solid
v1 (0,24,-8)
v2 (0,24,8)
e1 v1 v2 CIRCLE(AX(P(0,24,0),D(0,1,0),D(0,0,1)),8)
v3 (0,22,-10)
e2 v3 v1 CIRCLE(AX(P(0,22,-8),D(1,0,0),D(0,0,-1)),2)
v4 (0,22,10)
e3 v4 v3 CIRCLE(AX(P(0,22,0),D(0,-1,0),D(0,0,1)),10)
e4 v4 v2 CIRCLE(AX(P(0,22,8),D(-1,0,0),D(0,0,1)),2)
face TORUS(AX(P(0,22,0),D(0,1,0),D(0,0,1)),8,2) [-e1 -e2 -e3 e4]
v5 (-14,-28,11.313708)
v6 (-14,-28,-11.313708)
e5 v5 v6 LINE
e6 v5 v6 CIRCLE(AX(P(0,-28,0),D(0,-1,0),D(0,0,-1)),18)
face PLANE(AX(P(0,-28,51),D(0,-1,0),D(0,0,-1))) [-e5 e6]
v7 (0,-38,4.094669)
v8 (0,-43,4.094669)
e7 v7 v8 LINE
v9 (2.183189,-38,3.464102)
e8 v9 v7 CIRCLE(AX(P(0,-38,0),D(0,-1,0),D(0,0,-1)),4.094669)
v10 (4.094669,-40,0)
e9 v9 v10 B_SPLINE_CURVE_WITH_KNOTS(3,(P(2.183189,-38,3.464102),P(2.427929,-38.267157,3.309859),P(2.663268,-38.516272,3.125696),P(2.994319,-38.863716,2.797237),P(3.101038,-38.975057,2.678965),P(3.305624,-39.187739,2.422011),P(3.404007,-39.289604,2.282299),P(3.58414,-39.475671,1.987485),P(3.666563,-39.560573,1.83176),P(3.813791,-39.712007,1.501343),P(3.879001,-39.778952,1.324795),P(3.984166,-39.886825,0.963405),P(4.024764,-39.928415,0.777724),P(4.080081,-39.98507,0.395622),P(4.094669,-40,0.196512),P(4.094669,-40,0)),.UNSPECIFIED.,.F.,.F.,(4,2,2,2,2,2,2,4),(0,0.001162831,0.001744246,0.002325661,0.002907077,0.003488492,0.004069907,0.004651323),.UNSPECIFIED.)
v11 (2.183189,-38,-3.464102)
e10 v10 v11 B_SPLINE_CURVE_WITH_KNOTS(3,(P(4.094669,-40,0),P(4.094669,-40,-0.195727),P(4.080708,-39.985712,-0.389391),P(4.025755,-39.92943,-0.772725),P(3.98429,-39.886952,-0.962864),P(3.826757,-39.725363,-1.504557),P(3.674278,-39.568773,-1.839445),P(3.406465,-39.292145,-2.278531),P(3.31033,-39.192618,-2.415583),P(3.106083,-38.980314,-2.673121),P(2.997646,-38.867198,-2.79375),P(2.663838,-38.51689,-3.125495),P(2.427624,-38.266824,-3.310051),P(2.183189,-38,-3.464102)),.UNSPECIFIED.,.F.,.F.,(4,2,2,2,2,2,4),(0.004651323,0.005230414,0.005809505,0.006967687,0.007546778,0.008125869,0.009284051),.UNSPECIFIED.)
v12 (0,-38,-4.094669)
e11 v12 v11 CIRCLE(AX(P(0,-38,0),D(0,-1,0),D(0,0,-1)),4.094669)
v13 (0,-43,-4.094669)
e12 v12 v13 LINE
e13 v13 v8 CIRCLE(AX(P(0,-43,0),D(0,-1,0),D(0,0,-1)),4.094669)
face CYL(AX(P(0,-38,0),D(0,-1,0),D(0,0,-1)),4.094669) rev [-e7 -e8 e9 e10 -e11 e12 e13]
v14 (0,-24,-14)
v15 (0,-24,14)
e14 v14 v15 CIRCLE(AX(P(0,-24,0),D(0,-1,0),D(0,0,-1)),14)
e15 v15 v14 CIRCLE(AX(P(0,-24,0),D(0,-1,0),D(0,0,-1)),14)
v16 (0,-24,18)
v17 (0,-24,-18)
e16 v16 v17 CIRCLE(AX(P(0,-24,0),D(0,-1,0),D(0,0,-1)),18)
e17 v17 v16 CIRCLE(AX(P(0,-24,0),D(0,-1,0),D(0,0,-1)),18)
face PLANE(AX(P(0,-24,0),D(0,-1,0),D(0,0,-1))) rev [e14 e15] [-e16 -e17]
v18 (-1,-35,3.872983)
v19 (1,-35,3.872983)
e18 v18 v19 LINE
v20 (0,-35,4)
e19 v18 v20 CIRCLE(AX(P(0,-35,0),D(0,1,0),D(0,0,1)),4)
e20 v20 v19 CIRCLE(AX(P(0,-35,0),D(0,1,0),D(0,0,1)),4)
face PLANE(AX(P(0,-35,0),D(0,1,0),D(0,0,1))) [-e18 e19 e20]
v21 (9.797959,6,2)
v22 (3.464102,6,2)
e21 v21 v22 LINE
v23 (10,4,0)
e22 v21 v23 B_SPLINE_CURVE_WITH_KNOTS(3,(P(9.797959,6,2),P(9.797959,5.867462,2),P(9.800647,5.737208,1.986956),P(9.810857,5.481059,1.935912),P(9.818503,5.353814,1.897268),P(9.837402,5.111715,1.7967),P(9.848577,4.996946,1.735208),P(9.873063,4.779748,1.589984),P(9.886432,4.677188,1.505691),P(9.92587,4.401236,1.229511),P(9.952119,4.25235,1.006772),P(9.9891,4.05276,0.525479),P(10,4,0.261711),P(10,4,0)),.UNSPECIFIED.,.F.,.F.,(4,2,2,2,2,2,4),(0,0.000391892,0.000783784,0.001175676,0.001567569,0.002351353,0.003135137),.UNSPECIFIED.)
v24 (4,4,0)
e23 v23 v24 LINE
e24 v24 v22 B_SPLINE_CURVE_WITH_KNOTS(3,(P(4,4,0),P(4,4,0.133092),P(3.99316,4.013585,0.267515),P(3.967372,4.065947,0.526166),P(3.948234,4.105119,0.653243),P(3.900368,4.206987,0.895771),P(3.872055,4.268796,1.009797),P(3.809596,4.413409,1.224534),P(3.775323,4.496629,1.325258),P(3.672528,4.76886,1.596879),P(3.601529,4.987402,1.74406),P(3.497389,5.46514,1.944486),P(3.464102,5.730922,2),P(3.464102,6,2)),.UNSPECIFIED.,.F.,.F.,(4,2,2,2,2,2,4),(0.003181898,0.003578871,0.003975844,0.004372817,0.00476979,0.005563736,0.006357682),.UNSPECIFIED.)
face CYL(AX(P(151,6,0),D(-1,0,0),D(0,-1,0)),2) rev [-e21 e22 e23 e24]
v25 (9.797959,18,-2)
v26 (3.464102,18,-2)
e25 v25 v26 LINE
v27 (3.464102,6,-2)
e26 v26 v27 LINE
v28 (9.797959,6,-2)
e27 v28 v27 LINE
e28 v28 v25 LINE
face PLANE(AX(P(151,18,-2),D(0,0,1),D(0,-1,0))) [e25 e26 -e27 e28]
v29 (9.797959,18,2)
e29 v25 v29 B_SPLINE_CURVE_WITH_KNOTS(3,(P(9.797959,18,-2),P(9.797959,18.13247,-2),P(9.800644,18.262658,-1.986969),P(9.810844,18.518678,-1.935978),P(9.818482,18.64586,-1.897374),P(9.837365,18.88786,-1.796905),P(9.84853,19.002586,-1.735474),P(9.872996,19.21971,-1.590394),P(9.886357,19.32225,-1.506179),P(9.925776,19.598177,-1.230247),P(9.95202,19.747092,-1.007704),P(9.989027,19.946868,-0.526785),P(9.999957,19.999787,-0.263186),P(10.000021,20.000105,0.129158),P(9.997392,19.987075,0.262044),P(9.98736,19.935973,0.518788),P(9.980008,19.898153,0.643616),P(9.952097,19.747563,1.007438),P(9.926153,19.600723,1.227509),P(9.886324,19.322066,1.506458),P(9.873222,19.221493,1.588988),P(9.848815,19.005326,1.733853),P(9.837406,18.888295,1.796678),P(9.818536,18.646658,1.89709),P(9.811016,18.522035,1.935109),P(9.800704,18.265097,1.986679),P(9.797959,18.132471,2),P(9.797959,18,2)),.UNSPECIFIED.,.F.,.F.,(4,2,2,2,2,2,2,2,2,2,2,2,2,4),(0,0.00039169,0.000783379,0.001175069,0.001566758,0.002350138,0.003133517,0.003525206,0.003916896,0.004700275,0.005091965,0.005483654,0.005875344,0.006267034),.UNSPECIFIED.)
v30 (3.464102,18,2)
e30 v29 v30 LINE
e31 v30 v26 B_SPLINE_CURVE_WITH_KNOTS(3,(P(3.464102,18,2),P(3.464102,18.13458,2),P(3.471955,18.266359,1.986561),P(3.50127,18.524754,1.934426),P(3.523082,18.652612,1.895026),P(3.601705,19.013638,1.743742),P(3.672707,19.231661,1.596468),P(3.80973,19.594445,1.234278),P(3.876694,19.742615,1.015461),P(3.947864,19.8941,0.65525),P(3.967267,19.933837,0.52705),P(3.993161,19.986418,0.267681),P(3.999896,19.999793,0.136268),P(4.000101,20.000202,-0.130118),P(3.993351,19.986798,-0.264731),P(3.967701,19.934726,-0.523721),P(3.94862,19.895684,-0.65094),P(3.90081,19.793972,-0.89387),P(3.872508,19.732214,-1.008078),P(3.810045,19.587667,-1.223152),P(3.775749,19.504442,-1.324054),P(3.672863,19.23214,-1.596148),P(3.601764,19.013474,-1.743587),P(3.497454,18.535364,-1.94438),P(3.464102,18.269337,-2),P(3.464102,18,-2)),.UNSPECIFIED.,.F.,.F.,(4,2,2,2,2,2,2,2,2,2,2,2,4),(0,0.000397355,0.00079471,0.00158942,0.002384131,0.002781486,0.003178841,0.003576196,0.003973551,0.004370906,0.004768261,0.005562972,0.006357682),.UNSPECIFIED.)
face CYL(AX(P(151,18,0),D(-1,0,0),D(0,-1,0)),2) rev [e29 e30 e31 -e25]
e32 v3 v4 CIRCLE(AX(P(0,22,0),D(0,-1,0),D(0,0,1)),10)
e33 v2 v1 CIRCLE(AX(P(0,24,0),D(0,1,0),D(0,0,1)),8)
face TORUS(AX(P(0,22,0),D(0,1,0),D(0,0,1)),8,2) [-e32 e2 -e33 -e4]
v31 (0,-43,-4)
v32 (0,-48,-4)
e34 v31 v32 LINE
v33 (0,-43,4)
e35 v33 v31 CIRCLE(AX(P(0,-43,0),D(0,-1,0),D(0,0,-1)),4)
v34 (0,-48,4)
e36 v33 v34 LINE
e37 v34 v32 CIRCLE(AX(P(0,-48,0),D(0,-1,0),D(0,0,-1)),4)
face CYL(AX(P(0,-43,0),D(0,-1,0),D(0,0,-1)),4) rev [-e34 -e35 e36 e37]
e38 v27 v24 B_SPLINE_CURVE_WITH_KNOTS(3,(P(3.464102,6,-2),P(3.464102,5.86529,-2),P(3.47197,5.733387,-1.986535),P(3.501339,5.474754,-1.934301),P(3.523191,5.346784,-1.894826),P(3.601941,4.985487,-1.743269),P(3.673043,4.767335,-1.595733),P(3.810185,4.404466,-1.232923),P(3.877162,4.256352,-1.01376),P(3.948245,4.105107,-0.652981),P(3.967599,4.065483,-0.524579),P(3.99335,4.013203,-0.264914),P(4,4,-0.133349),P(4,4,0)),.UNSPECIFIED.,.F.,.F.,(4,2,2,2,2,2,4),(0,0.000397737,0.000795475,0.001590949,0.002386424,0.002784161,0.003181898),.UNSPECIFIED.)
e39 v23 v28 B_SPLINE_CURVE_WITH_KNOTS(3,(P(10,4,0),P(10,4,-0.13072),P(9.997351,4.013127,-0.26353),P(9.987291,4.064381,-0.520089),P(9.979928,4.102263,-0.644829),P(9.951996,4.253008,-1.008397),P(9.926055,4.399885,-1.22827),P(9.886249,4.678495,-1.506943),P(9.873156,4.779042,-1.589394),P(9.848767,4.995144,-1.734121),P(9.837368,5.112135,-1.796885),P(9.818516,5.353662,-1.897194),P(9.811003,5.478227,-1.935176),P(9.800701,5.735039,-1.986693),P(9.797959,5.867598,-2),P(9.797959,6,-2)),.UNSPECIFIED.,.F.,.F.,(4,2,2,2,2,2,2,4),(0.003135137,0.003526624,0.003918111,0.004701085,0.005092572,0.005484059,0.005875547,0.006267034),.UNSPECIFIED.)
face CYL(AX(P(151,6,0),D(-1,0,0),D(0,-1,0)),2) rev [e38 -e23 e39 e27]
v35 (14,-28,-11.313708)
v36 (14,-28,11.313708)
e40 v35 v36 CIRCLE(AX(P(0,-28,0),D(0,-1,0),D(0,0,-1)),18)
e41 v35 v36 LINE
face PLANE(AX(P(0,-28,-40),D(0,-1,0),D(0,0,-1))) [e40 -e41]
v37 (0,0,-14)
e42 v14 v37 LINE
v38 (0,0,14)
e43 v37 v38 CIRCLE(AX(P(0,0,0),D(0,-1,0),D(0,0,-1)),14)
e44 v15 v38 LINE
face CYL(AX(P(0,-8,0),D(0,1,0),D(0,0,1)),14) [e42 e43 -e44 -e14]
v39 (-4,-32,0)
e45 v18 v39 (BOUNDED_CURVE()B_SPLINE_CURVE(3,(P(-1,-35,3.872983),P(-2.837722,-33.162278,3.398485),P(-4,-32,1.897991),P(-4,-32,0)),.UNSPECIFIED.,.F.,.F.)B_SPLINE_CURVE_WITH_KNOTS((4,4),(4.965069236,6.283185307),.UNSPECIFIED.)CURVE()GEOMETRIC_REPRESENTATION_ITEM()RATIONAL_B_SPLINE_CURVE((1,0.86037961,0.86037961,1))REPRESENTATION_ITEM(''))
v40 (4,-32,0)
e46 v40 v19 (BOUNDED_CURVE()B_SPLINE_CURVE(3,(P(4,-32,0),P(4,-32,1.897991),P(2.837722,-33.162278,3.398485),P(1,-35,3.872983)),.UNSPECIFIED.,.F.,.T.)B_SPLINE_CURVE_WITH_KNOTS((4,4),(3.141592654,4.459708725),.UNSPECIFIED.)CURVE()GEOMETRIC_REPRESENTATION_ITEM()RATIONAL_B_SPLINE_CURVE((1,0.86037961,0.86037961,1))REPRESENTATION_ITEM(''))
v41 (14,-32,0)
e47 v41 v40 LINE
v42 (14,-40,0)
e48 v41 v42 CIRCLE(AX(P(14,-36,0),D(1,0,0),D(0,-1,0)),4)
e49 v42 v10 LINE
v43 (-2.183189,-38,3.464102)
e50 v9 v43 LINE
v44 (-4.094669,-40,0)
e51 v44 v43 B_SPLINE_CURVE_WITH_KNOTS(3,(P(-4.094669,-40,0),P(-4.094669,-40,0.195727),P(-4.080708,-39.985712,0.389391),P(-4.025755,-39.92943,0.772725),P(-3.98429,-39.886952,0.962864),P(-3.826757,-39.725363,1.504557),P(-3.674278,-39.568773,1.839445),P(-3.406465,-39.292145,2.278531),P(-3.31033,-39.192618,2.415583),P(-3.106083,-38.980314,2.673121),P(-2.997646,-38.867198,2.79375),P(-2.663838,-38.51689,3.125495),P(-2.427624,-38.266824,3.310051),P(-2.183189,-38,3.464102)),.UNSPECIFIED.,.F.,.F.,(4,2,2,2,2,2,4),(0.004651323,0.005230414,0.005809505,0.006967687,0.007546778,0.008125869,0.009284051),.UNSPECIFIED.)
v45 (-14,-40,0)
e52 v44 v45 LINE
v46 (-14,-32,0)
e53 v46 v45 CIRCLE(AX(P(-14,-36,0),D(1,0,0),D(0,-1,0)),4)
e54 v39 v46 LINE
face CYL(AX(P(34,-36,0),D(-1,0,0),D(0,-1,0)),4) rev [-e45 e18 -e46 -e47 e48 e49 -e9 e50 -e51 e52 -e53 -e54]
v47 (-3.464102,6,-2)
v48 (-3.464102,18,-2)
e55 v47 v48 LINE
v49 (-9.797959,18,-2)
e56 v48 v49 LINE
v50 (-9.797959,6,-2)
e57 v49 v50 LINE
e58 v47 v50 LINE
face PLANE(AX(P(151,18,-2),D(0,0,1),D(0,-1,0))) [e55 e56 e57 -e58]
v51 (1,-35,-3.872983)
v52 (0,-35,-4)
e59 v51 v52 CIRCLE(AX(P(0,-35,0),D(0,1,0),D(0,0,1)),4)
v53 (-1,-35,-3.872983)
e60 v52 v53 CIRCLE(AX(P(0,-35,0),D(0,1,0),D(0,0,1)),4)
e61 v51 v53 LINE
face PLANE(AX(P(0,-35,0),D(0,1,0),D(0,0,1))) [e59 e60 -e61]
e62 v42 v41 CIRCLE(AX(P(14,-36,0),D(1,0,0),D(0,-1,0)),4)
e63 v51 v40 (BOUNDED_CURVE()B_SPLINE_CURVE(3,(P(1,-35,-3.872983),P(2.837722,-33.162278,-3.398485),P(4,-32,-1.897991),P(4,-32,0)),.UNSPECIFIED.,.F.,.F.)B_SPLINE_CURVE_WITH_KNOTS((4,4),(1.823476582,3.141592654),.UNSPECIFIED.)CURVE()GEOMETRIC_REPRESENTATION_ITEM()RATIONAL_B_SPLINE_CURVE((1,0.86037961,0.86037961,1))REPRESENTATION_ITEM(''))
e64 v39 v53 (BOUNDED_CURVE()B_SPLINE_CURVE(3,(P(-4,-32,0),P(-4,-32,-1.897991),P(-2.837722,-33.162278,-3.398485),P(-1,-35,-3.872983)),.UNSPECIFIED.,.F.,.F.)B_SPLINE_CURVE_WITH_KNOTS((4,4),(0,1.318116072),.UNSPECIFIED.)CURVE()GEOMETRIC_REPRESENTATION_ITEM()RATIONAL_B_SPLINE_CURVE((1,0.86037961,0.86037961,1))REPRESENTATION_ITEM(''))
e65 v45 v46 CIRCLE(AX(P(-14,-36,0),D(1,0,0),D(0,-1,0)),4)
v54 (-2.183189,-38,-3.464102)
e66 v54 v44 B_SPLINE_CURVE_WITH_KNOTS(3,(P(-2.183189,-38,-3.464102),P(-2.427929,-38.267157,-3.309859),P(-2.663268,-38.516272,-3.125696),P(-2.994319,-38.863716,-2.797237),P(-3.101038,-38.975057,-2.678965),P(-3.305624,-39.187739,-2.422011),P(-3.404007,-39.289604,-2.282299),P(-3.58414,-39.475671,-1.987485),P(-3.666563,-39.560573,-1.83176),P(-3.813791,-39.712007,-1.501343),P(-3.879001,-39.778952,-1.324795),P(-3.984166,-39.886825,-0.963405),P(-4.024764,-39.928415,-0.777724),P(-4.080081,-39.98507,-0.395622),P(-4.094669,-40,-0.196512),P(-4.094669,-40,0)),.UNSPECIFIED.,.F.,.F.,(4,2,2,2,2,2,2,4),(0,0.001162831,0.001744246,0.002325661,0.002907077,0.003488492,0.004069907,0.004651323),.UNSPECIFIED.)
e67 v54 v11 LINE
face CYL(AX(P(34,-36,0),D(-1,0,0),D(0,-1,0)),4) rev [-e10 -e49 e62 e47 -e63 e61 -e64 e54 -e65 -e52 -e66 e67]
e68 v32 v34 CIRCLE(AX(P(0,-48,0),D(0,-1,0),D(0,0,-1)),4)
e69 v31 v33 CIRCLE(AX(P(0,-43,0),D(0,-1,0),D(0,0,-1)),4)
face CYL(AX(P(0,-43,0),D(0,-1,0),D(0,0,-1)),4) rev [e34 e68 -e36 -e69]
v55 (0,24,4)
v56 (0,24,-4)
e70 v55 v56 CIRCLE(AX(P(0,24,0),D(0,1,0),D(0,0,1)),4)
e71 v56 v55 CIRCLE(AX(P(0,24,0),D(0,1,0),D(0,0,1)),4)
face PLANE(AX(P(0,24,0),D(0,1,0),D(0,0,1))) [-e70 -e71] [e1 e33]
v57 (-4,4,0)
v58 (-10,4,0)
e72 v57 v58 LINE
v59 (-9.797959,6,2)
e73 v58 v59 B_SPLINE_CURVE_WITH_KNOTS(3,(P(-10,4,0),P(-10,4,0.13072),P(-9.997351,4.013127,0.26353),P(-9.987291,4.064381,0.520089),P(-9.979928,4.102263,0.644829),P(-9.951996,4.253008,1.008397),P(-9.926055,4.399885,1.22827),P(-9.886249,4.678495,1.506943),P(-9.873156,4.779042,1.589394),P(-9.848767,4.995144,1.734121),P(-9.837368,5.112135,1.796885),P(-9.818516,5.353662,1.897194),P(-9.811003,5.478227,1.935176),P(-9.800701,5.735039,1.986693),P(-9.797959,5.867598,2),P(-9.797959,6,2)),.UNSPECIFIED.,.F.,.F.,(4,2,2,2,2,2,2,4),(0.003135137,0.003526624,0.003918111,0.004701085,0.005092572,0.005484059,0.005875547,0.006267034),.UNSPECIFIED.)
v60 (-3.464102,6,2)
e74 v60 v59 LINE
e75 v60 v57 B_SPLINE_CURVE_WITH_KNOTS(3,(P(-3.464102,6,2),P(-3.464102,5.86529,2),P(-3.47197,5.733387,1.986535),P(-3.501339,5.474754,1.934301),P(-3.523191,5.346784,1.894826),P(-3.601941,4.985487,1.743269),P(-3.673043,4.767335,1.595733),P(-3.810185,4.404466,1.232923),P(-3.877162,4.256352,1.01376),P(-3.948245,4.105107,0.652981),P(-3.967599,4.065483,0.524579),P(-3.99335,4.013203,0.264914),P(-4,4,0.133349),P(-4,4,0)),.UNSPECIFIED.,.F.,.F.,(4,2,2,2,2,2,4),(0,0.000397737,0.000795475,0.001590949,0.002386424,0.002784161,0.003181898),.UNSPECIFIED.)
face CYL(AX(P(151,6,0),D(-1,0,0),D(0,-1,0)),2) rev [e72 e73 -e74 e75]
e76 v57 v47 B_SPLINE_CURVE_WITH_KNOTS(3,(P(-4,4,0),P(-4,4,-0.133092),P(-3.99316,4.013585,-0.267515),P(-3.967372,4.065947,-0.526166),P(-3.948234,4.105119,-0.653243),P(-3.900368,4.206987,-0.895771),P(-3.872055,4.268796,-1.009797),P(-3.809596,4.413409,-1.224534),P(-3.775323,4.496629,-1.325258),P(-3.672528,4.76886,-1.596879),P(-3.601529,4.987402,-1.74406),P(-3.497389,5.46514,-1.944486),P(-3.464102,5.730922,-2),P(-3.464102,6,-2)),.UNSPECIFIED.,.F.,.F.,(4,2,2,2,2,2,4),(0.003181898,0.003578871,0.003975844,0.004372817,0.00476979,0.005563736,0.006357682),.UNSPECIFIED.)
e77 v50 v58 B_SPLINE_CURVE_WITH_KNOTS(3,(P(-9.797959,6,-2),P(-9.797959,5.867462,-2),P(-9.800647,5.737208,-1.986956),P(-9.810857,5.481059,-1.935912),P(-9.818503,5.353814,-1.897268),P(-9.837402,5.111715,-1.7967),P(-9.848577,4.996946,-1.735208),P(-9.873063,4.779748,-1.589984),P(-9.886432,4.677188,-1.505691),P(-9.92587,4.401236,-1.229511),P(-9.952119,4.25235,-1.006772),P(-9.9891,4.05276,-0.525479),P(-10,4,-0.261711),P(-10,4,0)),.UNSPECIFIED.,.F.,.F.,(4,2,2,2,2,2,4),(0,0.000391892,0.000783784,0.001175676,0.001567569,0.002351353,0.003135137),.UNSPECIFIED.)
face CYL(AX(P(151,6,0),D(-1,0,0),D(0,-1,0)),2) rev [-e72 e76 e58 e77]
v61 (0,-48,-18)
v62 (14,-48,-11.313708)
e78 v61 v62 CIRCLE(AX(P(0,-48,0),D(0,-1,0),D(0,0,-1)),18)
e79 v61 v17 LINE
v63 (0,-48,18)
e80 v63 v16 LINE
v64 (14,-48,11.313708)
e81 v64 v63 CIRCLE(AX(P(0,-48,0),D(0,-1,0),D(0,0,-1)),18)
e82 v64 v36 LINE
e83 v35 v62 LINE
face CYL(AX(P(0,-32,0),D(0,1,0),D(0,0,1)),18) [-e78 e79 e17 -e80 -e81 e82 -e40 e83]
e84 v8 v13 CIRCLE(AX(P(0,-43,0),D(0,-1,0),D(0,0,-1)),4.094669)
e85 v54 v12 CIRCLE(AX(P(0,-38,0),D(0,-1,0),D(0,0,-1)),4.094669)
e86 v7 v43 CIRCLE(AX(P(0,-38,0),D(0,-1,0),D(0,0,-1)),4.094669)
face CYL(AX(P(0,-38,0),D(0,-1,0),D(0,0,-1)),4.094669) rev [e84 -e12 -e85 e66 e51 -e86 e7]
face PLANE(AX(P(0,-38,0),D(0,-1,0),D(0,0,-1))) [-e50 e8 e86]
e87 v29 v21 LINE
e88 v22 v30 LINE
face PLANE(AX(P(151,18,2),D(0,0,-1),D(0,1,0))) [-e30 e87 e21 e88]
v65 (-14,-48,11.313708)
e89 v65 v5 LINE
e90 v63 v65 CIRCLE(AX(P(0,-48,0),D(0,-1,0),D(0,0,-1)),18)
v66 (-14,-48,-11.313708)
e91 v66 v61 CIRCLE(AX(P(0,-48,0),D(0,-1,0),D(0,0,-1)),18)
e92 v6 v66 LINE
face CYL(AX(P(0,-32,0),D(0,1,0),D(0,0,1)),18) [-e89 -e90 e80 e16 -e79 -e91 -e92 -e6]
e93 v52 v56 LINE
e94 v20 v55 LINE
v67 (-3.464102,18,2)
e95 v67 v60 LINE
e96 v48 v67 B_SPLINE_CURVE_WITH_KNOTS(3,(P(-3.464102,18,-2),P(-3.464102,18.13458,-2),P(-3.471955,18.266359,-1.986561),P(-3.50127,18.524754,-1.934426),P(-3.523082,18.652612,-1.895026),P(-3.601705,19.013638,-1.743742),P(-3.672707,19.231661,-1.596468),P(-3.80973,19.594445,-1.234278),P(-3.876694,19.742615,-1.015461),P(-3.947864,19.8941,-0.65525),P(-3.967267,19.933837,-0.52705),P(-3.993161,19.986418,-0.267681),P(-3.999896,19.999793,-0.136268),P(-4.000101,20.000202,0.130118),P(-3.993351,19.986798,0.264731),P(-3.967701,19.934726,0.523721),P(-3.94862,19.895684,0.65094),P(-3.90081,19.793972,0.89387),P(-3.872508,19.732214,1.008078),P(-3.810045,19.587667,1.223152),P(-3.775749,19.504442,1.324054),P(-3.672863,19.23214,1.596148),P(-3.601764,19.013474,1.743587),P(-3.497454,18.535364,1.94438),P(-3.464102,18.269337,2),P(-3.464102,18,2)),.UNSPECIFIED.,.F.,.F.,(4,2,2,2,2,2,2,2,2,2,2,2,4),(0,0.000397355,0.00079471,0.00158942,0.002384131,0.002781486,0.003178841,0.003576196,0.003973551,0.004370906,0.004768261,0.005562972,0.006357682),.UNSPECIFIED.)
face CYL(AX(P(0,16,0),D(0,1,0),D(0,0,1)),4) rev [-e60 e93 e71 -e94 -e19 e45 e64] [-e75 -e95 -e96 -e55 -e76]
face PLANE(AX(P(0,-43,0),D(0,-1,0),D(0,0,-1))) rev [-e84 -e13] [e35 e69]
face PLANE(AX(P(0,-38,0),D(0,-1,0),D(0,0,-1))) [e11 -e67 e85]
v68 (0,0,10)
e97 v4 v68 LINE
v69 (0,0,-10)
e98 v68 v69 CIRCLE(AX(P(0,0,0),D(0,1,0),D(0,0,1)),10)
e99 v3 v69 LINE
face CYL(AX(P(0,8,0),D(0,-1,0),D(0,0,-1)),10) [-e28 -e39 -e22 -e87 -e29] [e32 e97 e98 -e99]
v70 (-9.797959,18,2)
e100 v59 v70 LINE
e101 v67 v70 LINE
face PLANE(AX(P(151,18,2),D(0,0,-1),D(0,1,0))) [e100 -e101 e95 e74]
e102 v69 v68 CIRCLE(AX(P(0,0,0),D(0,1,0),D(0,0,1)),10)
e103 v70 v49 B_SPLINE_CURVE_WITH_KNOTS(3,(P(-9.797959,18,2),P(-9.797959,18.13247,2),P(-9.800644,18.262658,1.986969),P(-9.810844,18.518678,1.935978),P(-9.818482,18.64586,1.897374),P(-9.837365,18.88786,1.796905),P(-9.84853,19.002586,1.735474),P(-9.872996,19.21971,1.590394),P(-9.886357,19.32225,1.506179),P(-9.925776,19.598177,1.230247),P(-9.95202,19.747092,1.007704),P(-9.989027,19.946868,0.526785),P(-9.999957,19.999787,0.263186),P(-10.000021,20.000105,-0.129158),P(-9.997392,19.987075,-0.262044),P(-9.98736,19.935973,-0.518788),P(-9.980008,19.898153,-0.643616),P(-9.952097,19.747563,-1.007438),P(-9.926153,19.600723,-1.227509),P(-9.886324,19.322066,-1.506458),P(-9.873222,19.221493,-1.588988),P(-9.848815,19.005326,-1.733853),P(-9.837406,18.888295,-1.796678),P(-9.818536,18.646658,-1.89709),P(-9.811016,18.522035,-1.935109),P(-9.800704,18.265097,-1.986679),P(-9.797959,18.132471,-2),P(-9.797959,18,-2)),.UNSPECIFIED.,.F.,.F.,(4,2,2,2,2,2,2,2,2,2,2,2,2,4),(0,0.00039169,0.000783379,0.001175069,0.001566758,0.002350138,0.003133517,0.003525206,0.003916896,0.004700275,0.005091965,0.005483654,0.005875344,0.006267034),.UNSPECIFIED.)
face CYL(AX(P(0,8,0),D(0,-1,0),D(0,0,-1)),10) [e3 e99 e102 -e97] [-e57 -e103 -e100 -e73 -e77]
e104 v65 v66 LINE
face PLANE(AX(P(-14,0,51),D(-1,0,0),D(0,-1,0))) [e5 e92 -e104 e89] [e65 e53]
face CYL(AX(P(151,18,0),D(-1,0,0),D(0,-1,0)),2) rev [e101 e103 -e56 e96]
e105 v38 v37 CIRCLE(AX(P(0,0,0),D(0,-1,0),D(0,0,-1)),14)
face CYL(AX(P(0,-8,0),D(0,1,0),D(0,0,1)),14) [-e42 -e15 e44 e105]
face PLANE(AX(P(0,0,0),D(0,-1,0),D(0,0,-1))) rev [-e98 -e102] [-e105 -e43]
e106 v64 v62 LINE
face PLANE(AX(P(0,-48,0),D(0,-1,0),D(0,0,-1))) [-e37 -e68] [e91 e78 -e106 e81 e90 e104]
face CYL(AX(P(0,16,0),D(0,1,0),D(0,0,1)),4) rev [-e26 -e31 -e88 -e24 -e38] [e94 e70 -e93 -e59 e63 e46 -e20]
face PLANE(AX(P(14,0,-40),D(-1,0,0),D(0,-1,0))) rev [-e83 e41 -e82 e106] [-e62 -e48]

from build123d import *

# Parameters (mm, degrees)
SHANK_20_SKETCH_R          = 10
SHANK_20_STEP_1_DEPTH      = 8
SHANK_STEP_2_SKETCH_R      = 10
SHANK_20_STEP_2_DEPTH      = 8
SHANK_STEP_3_SKETCH_R      = 10
SHANK_20_STEP_3_DEPTH      = 8
SHANK_END_FILLET_R2_R      = 2
SHANK_BORE_8_SKETCH_R      = 4
SHANK_BORE_8_CUT_1_DEPTH   = 8
SHANK_BORE_CUT_2_SKETCH_R  = 4
SHANK_BORE_8_CUT_2_DEPTH   = 8
SHANK_BORE_CUT_3_SKETCH_R  = 4
SHANK_BORE_8_CUT_3_DEPTH   = 18
COLLAR_28_SKETCH_R         = 14
COLLAR_28_STEP_1_DEPTH     = 8
COLLAR_STEP_2_SKETCH_R     = 14
COLLAR_28_STEP_2_DEPTH     = 8
COLLAR_STEP_3_SKETCH_R     = 14
COLLAR_28_STEP_3_DEPTH     = 8
HEAD_36_SKETCH_R           = 18
HEAD_36_STEP_1_DEPTH       = 8
HEAD_STEP_2_SKETCH_R       = 18
HEAD_36_STEP_2_DEPTH       = 8
HEAD_STEP_3_SKETCH_R       = 18
HEAD_36_STEP_3_DEPTH       = 8
HEAD_FLAT_DEPTH            = 51
HEAD_FLAT_DEPTH_BACK       = 40
HEAD_FLAT_SKETCH_W         = 4
HEAD_FLAT_SKETCH_H         = 20
CROSS_HOLE_8_DEPTH         = 20
CROSS_HOLE_8_DEPTH_BACK    = 52
CROSS_HOLE_8_SKETCH_R      = 4
COLLAR_BORE_CUT_1_SKETCH_R = 4
COLLAR_BORE_CUT_1_DEPTH    = 5
COLLAR_BORE_CUT_2_SKETCH_R = 4
COLLAR_BORE_CUT_2_DEPTH    = 5
COLLAR_BORE_CUT_3_SKETCH_R = 4
COLLAR_BORE_CUT_3_DEPTH    = 5
HEAD_START                 = -5
HEAD_BORE_8_SKETCH_R       = 4
HEAD_BORE_8_CUT_1_DEPTH    = 5
HEAD_BORE_CUT_2_SKETCH_R   = 4.094669118
HEAD_BORE_8_CUT_2_DEPTH    = 5
COLLAR_BORE_CUT_4_SKETCH_R = 4
COLLAR_BORE_CUT_4_DEPTH    = 5
INNER_BORE_8_SKETCH_R      = 4
INNER_BORE_8_CUT_1_DEPTH   = 5
INNER_BORE_CUT_2_SKETCH_R  = 4
INNER_BORE_8_CUT_2_DEPTH   = 5
INNER_BORE_CUT_3_SKETCH_R  = 4
INNER_BORE_8_CUT_3_DEPTH   = 5
SHANK_SLOT_DEPTH           = 137
SHANK_SLOT_DEPTH_BACK      = 146


with BuildPart() as part:
    # Shank Ø20 Sketch → Shank Ø20 Step 1 (new body)
    with BuildSketch(Plane(origin=(0, 0, 0), x_dir=(1, 0, 0), z_dir=(0, 1, 0))):
        with Locations(Location((0, 0, 0), (0, 0, 270))):
            Circle(SHANK_20_SKETCH_R)
    extrude(amount=SHANK_20_STEP_1_DEPTH)

    # Shank Step 2 Sketch → Shank Ø20 Step 2 (add)
    with BuildSketch(Plane(origin=(0, 8, 0), x_dir=(1, 0, 0), z_dir=(0, 1, 0))):
        with Locations(Location((0, 0, 0), (0, 0, 270))):
            Circle(SHANK_STEP_2_SKETCH_R)
    extrude(amount=SHANK_20_STEP_2_DEPTH)

    # Shank Step 3 Sketch → Shank Ø20 Step 3 (add)
    with BuildSketch(Plane(origin=(0, 16, 0), x_dir=(1, 0, 0), z_dir=(0, 1, 0))):
        with Locations(Location((0, 0, 0), (0, 0, 270))):
            Circle(SHANK_STEP_3_SKETCH_R)
    extrude(amount=SHANK_20_STEP_3_DEPTH)

    # Shank End Fillet R2
    shank_end_fillet_r2_edges = [part.edges().sort_by_distance(p)[0] for p in [
        (0, 24, -10),
    ]]
    fillet(shank_end_fillet_r2_edges, radius=SHANK_END_FILLET_R2_R)

    # Shank Bore Ø8 Sketch → Shank Bore Ø8 Cut 1 (cut)
    with BuildSketch(Plane(origin=(0, 24, 0), x_dir=(1, 0, 0), z_dir=(0, 1, 0))):
        with Locations(Location((0, 0, 0), (0, 0, 270))):
            Circle(SHANK_BORE_8_SKETCH_R)
    extrude(amount=-SHANK_BORE_8_CUT_1_DEPTH, mode=Mode.SUBTRACT)

    # Shank Bore Cut 2 Sketch → Shank Bore Ø8 Cut 2 (cut)
    with BuildSketch(Plane(origin=(0, 16, 0), x_dir=(1, 0, 0), z_dir=(0, 1, 0))):
        with Locations(Location((0, 0, 0), (0, 0, 270))):
            Circle(SHANK_BORE_CUT_2_SKETCH_R)
    extrude(amount=-SHANK_BORE_8_CUT_2_DEPTH, mode=Mode.SUBTRACT)

    # Shank Bore Cut 3 Sketch → Shank Bore Ø8 Cut 3 (cut)
    with BuildSketch(Plane(origin=(0, 8, 0), x_dir=(1, 0, 0), z_dir=(0, 1, 0))):
        with Locations(Location((0, 0, 0), (0, 0, 270))):
            Circle(SHANK_BORE_CUT_3_SKETCH_R)
    extrude(amount=-SHANK_BORE_8_CUT_3_DEPTH, mode=Mode.SUBTRACT)

    # Collar Ø28 Sketch → Collar Ø28 Step 1 (add)
    with BuildSketch(Plane.XZ):
        with Locations(Location((0, 0, 0), (0, 0, 270))):
            Circle(COLLAR_28_SKETCH_R)
    extrude(amount=COLLAR_28_STEP_1_DEPTH)

    # Collar Step 2 Sketch → Collar Ø28 Step 2 (add)
    with BuildSketch(Plane.XZ.offset(8)):
        with Locations(Location((0, 0, 0), (0, 0, 270))):
            Circle(COLLAR_STEP_2_SKETCH_R)
    extrude(amount=COLLAR_28_STEP_2_DEPTH)

    # Collar Step 3 Sketch → Collar Ø28 Step 3 (add)
    with BuildSketch(Plane.XZ.offset(16)):
        with Locations(Location((0, 0, 0), (0, 0, 270))):
            Circle(COLLAR_STEP_3_SKETCH_R)
    extrude(amount=COLLAR_28_STEP_3_DEPTH)

    # Head Ø36 Sketch → Head Ø36 Step 1 (add)
    with BuildSketch(Plane.XZ.offset(24)):
        with Locations(Location((0, 0, 0), (0, 0, 270))):
            Circle(HEAD_36_SKETCH_R)
    extrude(amount=HEAD_36_STEP_1_DEPTH)

    # Head Step 2 Sketch → Head Ø36 Step 2 (add)
    with BuildSketch(Plane.XZ.offset(32)):
        with Locations(Location((0, 0, 0), (0, 0, 270))):
            Circle(HEAD_STEP_2_SKETCH_R)
    extrude(amount=HEAD_36_STEP_2_DEPTH)

    # Head Step 3 Sketch → Head Ø36 Step 3 (add)
    with BuildSketch(Plane.XZ.offset(40)):
        with Locations(Location((0, 0, 0), (0, 0, 270))):
            Circle(HEAD_STEP_3_SKETCH_R)
    extrude(amount=HEAD_36_STEP_3_DEPTH)

    # Head Flat Sketch → Head Flat (cut, two sides: drawn at the far end of the back side and taken through both)
    with BuildSketch(Plane.XY.offset(-HEAD_FLAT_DEPTH_BACK)):
        with Locations((-16, -38)):
            Rectangle(HEAD_FLAT_SKETCH_W, HEAD_FLAT_SKETCH_H)
        with Locations((16, -38)):
            Rectangle(HEAD_FLAT_SKETCH_W, HEAD_FLAT_SKETCH_H)
    extrude(amount=HEAD_FLAT_DEPTH + HEAD_FLAT_DEPTH_BACK, mode=Mode.SUBTRACT)

    # Cross Hole Ø8 Sketch → Cross Hole Ø8 (cut, two sides: drawn at the far end of the back side and taken through both)
    with BuildSketch(Plane(origin=(14, 0, 0), x_dir=(0, 0, -1), z_dir=(1, 0, 0)).offset(-CROSS_HOLE_8_DEPTH_BACK)):
        with Locations(Location((0, -36, 0), (0, 0, 270))):
            Circle(CROSS_HOLE_8_SKETCH_R)
    extrude(amount=CROSS_HOLE_8_DEPTH + CROSS_HOLE_8_DEPTH_BACK, mode=Mode.SUBTRACT)

    # Collar Bore Cut 1 Sketch → Collar Bore Cut 1 (cut)
    with BuildSketch(Plane(origin=(0, 0, 0), x_dir=(1, 0, 0), z_dir=(0, 1, 0))):
        with Locations(Location((0, 0, 0), (0, 0, 270))):
            Circle(COLLAR_BORE_CUT_1_SKETCH_R)
    extrude(amount=-COLLAR_BORE_CUT_1_DEPTH, mode=Mode.SUBTRACT)

    # Collar Bore Cut 2 Sketch → Collar Bore Cut 2 (cut)
    with BuildSketch(Plane(origin=(0, -5, 0), x_dir=(1, 0, 0), z_dir=(0, 1, 0))):
        with Locations(Location((0, 0, 0), (0, 0, 270))):
            Circle(COLLAR_BORE_CUT_2_SKETCH_R)
    extrude(amount=-COLLAR_BORE_CUT_2_DEPTH, mode=Mode.SUBTRACT)

    # Collar Bore Cut 3 Sketch → Collar Bore Cut 3 (cut)
    with BuildSketch(Plane(origin=(0, -10, 0), x_dir=(1, 0, 0), z_dir=(0, 1, 0))):
        with Locations(Location((0, 0, 0), (0, 0, 270))):
            Circle(COLLAR_BORE_CUT_3_SKETCH_R)
    extrude(amount=-COLLAR_BORE_CUT_3_DEPTH, mode=Mode.SUBTRACT)

    # Head Bore Ø8 Sketch → Head Bore Ø8 Cut 1 (cut)
    with BuildSketch(Plane.XZ.offset(48).offset(HEAD_START)):
        with Locations(Location((0, 0, 0), (0, 0, 90))):
            Circle(HEAD_BORE_8_SKETCH_R)
    extrude(amount=HEAD_BORE_8_CUT_1_DEPTH, mode=Mode.SUBTRACT)

    # Head Bore Cut 2 Sketch → Head Bore Ø8 Cut 2 (cut)
    with BuildSketch(Plane.XZ.offset(43)):
        with Locations(Location((0, 0, 0), (0, 0, 270))):
            Circle(HEAD_BORE_CUT_2_SKETCH_R)
    extrude(amount=-HEAD_BORE_8_CUT_2_DEPTH, mode=Mode.SUBTRACT)

    # Collar Bore Cut 4 Sketch → Collar Bore Cut 4 (cut)
    with BuildSketch(Plane(origin=(0, -15, 0), x_dir=(1, 0, 0), z_dir=(0, 1, 0))):
        with Locations(Location((0, 0, 0), (0, 0, 270))):
            Circle(COLLAR_BORE_CUT_4_SKETCH_R)
    extrude(amount=-COLLAR_BORE_CUT_4_DEPTH, mode=Mode.SUBTRACT)

    # Inner Bore Ø8 Sketch → Inner Bore Ø8 Cut 1 (cut)
    with BuildSketch(Plane(origin=(0, -20, 0), x_dir=(1, 0, 0), z_dir=(0, 1, 0))):
        with Locations(Location((0, 0, 0), (0, 0, 270))):
            Circle(INNER_BORE_8_SKETCH_R)
    extrude(amount=-INNER_BORE_8_CUT_1_DEPTH, mode=Mode.SUBTRACT)

    # Inner Bore Cut 2 Sketch → Inner Bore Ø8 Cut 2 (cut)
    with BuildSketch(Plane(origin=(0, -25, 0), x_dir=(1, 0, 0), z_dir=(0, 1, 0))):
        with Locations(Location((0, 0, 0), (0, 0, 270))):
            Circle(INNER_BORE_CUT_2_SKETCH_R)
    extrude(amount=-INNER_BORE_8_CUT_2_DEPTH, mode=Mode.SUBTRACT)

    # Inner Bore Cut 3 Sketch → Inner Bore Ø8 Cut 3 (cut)
    with BuildSketch(Plane(origin=(0, -30, 0), x_dir=(1, 0, 0), z_dir=(0, 1, 0))):
        with Locations(Location((0, 0, 0), (0, 0, 270))):
            Circle(INNER_BORE_CUT_3_SKETCH_R)
    extrude(amount=-INNER_BORE_8_CUT_3_DEPTH, mode=Mode.SUBTRACT)

    # Shank Slot Sketch → Shank Slot (cut, two sides: drawn at the far end of the back side and taken through both)
    with BuildSketch(Plane(origin=(14, 0, 0), x_dir=(0, 0, -1), z_dir=(1, 0, 0)).offset(-SHANK_SLOT_DEPTH_BACK)):
        with BuildLine():
            Line((-2, 18), (-2, 6))
            ThreePointArc((-2, 6), (0, 4), (2, 6))
            Line((2, 6), (2, 18))
            ThreePointArc((2, 18), (0, 20), (-2, 18))
        make_face()
    extrude(amount=SHANK_SLOT_DEPTH + SHANK_SLOT_DEPTH_BACK, mode=Mode.SUBTRACT)


solid = part.part
